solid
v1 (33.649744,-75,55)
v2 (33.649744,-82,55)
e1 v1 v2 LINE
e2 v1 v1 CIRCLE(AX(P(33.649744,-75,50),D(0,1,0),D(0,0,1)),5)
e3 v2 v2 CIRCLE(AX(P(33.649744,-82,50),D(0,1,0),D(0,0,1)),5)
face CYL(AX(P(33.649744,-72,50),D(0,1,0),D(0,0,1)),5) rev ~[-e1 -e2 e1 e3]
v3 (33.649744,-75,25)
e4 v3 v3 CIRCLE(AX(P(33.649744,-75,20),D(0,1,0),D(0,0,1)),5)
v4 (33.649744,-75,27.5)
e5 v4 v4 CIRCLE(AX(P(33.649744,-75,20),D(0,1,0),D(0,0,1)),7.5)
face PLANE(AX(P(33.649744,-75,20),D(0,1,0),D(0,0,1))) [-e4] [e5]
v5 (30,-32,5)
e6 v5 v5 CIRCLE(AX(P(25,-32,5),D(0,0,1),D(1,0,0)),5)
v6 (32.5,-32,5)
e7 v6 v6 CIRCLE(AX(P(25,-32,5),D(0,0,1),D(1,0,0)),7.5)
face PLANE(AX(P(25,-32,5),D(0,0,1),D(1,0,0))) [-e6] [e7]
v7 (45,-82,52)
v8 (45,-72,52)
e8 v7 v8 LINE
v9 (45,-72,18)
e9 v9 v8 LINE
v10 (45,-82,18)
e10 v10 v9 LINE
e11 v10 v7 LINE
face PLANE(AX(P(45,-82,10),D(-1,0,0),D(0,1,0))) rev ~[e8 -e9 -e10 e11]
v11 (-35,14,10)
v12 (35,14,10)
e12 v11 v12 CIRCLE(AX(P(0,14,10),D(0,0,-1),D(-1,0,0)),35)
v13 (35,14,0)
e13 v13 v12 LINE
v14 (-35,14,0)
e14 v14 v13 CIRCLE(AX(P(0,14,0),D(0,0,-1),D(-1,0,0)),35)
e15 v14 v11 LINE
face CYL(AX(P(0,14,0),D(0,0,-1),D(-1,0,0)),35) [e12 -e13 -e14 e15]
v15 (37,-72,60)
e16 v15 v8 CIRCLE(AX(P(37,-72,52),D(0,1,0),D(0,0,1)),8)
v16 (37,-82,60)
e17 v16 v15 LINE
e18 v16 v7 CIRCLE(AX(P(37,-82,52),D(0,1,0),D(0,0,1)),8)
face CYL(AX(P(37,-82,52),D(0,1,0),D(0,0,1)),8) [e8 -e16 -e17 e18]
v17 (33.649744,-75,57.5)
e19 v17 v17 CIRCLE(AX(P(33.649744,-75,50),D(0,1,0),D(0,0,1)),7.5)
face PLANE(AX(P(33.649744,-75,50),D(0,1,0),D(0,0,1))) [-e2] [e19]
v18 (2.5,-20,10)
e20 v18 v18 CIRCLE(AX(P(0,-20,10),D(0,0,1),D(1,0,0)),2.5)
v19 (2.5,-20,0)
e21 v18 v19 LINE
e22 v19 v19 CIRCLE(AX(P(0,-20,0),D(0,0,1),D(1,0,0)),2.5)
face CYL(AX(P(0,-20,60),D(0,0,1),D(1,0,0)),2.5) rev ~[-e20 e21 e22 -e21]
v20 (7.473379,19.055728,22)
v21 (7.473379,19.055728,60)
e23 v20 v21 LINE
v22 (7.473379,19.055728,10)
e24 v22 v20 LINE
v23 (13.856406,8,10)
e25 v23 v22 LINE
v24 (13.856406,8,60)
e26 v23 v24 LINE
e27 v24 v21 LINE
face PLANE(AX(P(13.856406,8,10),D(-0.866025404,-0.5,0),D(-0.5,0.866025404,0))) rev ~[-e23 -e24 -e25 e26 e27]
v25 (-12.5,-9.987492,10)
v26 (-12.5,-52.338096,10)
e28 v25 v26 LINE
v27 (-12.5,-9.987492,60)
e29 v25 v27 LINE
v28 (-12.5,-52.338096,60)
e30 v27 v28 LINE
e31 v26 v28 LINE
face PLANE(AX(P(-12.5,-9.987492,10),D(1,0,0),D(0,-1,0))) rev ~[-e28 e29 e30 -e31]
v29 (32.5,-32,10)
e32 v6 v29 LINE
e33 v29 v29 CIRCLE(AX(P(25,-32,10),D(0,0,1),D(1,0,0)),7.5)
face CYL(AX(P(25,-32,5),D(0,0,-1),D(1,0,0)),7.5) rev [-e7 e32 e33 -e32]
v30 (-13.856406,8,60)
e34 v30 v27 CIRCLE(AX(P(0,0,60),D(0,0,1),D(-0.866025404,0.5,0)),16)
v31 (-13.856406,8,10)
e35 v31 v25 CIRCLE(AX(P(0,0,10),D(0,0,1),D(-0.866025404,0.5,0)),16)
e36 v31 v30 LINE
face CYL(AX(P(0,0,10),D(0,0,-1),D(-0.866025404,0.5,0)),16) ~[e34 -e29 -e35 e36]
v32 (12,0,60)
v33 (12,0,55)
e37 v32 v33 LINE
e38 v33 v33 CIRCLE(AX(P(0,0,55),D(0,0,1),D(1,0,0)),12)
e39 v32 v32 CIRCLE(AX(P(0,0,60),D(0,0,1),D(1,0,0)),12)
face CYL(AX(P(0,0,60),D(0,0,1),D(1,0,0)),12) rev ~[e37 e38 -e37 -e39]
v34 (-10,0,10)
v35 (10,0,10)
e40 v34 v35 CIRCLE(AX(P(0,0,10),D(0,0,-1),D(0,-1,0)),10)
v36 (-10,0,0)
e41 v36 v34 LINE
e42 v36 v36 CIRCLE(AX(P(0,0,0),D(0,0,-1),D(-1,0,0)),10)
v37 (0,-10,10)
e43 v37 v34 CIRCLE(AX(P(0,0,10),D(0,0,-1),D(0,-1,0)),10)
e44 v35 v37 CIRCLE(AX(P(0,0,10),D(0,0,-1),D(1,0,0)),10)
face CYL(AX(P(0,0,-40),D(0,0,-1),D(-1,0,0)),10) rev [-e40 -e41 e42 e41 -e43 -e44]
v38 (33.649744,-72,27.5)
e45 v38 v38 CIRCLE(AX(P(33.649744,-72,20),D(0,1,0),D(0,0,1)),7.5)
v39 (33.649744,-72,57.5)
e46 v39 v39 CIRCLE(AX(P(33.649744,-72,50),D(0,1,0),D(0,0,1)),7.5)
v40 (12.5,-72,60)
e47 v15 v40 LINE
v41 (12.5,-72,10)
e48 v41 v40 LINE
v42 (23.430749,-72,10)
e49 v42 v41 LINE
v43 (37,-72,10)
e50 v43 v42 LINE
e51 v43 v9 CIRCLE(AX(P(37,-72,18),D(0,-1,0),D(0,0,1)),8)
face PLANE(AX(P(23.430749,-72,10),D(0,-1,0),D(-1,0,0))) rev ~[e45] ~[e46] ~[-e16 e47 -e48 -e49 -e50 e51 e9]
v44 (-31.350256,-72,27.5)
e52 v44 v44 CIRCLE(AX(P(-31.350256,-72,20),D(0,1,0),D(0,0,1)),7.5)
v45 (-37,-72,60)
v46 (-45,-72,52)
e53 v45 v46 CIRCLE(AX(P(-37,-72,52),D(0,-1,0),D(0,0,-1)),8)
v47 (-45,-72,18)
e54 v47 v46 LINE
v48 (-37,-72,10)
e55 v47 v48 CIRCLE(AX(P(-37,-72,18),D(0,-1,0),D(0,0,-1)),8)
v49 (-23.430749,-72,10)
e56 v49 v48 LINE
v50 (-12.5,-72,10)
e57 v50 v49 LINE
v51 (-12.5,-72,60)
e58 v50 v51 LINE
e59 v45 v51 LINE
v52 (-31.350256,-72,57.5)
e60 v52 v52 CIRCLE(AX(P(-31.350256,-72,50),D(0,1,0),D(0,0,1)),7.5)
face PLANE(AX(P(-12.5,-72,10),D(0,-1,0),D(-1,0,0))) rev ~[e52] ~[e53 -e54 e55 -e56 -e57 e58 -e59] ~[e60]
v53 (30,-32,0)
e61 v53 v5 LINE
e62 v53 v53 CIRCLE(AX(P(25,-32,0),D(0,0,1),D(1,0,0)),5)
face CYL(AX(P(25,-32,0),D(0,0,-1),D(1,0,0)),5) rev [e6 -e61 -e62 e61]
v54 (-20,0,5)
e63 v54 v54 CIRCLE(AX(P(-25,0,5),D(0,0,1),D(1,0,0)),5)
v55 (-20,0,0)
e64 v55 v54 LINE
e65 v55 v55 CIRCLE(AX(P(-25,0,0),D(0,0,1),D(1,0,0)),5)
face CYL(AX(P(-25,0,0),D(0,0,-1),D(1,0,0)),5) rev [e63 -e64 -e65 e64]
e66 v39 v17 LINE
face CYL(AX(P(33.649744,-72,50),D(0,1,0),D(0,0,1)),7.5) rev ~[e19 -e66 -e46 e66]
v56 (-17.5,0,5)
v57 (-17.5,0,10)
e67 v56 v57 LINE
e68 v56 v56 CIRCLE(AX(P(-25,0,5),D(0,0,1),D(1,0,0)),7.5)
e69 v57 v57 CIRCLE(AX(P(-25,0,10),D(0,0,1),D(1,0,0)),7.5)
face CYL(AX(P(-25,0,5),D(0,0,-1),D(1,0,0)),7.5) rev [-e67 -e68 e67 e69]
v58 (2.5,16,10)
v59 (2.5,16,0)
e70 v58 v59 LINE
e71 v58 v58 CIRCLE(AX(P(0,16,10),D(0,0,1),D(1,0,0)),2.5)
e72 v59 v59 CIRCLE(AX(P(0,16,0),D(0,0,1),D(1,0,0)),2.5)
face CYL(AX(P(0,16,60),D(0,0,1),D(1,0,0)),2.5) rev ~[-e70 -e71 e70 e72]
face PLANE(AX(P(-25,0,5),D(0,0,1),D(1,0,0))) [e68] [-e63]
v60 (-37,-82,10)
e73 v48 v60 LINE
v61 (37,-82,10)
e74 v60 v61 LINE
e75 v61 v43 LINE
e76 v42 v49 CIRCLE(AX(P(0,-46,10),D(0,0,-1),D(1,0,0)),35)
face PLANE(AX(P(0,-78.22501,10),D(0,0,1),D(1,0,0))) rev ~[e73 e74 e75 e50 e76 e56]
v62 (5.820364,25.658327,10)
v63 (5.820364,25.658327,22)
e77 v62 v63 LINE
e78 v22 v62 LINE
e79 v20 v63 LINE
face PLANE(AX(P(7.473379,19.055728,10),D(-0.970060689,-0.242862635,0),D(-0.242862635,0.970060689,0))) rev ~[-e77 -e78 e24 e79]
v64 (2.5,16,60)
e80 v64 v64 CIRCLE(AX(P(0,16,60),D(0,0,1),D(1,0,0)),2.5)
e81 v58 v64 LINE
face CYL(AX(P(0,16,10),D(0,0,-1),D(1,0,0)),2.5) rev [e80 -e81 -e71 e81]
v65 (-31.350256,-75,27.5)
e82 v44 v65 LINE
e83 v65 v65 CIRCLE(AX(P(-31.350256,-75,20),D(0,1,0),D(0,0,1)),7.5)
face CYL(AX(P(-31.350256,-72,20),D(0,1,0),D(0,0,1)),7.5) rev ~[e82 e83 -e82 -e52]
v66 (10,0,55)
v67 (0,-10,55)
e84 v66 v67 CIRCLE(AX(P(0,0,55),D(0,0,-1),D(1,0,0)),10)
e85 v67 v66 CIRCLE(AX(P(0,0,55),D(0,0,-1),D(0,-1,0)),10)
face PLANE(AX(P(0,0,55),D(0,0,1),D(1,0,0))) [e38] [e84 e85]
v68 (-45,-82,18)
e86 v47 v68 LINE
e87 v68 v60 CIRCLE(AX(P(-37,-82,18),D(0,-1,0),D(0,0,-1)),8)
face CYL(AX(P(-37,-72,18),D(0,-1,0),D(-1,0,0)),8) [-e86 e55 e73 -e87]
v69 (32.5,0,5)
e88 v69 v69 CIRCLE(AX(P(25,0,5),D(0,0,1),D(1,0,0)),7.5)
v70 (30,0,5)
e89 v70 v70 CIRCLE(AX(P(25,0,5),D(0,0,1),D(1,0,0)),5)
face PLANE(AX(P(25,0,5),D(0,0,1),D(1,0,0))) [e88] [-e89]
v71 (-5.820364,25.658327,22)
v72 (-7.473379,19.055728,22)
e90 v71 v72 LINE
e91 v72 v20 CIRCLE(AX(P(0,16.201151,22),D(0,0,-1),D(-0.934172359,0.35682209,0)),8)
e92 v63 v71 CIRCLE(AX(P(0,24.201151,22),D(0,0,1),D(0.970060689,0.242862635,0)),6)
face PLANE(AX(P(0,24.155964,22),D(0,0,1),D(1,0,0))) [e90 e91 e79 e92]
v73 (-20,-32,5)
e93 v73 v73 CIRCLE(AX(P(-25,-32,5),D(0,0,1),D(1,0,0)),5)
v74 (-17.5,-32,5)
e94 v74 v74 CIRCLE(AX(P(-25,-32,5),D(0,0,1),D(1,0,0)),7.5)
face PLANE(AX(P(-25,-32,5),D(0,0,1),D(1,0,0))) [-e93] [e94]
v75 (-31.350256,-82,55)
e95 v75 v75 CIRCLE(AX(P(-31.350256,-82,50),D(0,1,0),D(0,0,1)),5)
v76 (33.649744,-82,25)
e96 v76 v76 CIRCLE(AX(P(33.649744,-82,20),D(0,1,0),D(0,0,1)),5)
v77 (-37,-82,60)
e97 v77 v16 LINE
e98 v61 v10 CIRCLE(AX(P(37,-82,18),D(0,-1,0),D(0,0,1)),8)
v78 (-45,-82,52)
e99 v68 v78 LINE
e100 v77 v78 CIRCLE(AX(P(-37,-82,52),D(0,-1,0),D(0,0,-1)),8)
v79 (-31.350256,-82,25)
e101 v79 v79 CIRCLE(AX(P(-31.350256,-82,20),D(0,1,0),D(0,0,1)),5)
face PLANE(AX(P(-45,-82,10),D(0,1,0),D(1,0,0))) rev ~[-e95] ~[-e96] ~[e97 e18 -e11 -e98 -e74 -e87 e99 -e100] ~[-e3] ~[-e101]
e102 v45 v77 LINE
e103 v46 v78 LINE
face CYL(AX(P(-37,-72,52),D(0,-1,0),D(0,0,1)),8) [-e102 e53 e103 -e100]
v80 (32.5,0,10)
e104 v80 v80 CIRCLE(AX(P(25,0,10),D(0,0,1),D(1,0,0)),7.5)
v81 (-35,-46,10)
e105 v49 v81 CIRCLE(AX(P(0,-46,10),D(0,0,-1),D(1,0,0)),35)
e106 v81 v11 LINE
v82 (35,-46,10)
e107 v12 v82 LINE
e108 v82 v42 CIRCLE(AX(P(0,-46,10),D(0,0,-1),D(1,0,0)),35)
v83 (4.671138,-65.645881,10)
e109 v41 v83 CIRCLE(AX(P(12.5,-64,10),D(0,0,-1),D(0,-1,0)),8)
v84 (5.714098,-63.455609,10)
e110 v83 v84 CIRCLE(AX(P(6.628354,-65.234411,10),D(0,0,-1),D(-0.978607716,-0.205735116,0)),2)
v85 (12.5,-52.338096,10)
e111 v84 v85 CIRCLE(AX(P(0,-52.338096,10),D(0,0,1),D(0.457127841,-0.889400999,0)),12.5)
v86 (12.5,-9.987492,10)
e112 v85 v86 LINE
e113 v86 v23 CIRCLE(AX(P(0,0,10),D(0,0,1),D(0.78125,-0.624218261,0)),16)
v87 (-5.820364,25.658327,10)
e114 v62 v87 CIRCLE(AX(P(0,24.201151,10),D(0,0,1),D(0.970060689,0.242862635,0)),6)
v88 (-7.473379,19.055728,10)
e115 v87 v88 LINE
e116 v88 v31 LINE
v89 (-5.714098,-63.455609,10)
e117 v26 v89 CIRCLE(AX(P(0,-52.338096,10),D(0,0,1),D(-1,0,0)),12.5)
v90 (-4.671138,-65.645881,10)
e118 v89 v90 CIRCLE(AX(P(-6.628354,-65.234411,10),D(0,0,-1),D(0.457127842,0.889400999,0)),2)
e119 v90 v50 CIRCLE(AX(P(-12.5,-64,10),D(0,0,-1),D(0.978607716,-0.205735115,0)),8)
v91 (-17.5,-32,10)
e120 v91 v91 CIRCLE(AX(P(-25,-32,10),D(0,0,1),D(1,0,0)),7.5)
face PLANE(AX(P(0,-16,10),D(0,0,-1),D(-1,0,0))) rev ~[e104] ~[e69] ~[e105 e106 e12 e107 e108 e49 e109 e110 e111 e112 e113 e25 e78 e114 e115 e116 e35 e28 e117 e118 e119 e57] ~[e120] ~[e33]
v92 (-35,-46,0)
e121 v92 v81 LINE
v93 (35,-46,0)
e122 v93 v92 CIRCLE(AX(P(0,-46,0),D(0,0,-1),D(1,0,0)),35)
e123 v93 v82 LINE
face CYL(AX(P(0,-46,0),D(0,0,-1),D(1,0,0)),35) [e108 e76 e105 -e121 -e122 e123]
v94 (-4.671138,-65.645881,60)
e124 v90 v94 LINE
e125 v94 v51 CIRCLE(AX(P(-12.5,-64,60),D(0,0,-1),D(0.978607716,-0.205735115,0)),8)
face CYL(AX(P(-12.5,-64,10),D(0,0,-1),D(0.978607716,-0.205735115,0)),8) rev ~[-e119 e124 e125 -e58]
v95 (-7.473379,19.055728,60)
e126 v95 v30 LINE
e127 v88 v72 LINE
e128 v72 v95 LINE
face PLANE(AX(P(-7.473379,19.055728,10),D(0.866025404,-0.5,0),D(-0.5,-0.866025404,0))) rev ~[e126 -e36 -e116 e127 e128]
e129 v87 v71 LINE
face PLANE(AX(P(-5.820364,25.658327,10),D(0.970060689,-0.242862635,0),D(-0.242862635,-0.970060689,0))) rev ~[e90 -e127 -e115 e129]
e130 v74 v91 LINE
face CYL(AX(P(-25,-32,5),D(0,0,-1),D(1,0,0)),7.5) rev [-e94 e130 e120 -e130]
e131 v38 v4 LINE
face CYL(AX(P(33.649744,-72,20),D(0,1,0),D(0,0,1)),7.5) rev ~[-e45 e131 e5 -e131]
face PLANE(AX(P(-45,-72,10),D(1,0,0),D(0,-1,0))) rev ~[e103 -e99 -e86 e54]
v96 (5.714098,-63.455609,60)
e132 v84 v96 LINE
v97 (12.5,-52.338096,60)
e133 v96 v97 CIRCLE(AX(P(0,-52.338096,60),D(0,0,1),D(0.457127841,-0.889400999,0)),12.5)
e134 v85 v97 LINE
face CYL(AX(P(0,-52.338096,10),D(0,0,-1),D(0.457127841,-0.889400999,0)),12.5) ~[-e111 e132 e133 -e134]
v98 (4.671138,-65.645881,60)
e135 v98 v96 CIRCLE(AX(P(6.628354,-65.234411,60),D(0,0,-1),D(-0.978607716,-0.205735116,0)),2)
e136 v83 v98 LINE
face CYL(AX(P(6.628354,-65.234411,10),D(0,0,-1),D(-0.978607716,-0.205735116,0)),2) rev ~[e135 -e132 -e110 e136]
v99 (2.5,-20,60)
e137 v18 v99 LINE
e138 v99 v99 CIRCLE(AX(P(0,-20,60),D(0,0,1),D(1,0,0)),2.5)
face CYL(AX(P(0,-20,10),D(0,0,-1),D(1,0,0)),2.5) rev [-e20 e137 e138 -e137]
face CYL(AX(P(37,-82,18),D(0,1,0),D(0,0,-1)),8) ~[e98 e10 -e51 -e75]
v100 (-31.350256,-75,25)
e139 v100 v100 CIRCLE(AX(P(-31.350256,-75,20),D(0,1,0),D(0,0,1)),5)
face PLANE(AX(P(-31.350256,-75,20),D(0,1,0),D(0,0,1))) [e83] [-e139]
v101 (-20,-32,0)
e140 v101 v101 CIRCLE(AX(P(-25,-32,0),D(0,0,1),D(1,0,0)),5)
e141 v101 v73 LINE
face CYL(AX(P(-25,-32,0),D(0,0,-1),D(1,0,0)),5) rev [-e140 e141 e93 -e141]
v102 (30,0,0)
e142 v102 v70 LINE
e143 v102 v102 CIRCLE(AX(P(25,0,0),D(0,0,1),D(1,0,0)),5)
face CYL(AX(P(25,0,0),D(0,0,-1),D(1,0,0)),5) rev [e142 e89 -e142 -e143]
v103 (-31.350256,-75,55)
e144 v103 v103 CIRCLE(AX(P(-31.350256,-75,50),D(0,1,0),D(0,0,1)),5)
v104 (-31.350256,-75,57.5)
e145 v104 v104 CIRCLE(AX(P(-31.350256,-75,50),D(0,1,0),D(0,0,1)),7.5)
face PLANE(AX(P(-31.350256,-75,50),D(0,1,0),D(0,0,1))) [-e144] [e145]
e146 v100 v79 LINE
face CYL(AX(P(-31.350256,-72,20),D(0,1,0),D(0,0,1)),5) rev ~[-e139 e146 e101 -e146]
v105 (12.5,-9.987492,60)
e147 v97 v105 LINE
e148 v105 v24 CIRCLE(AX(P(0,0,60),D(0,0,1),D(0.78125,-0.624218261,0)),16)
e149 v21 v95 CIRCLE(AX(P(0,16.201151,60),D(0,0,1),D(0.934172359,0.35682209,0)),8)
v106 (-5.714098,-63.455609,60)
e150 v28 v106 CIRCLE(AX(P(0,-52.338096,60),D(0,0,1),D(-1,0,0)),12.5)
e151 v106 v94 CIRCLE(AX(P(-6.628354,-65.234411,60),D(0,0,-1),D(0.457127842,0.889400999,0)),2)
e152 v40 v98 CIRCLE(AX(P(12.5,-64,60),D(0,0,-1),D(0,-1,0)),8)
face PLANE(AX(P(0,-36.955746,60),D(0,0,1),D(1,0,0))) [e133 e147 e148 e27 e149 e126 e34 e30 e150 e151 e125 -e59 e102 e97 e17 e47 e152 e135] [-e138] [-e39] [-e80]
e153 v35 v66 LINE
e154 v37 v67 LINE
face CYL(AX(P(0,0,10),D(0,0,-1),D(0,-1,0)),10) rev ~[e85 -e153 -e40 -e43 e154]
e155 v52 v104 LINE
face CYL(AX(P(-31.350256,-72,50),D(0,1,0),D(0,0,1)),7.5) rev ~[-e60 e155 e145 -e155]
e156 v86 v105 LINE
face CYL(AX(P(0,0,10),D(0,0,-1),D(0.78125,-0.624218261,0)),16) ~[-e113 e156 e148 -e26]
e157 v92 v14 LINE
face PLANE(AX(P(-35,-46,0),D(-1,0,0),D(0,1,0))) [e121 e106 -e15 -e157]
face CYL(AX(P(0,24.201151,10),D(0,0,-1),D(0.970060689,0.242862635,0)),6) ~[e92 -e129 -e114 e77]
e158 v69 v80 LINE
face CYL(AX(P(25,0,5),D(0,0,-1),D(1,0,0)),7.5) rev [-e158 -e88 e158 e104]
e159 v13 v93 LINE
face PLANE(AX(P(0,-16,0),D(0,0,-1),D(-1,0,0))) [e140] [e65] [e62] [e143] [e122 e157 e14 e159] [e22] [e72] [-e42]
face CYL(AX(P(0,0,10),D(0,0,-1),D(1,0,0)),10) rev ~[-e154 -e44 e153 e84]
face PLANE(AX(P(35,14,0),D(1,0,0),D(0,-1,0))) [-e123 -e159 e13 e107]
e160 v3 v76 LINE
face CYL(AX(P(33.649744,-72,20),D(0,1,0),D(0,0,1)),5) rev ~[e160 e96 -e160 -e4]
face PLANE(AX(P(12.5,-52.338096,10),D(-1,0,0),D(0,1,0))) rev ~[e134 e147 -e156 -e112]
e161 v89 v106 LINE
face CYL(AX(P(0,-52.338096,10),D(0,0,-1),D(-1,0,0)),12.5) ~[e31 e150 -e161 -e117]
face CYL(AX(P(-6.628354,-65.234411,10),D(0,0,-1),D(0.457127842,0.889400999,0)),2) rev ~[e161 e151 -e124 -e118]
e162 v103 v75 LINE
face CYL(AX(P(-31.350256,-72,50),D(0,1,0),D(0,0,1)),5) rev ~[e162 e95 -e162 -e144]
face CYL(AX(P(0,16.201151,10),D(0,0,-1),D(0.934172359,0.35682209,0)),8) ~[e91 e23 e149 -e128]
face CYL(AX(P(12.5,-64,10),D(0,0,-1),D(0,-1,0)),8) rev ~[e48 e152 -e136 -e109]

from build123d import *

# Parameters (mm, degrees)
FLANGE_PLATE_SKETCH_R     = 5
FLANGE_PLATE_DEPTH        = 10
FLANGE_START              = -5
FLANGE_RECESS_SKETCH_R    = 7.5
FLANGE_RECESS_SKETCH_R_2  = 5
FLANGE_RECESS_5MM_DEPTH   = 5
BRACKET_BODY_SKETCH_R     = 2.5
BRACKET_BODY_DEPTH        = 50
THROUGH_START             = -50
THROUGH_BORE_SKETCH_R     = 10
THROUGH_BORE_DEPTH        = 50
BORE_COUNTERBORE_SKETCH_R = 12
BORE_COUNTERBORE_24_DEPTH = 5
BODY_POCKET_SKETCH_R      = 5
BODY_POCKET_20MM_DEPTH    = 20
POCKET_STEP_SKETCH_R      = 7.5
POCKET_STEP_3MM_DEPTH     = 3
BODY_BOSS_12MM_DEPTH      = 12
BODY_FILLET_R8_A_R        = 8
BODY_FILLET_R8_B_R        = 8
BODY_SLOT_SKETCH_R        = 2.5
BODY_SLOT_CUT_DEPTH       = 112.126054551


with BuildPart() as part:
    # Flange Plate Sketch → Flange Plate (new body)
    with BuildSketch(Plane.XY):
        with BuildLine():
            Line((-35, -46), (-35, 14))
            ThreePointArc((-35, 14), (0, 49), (35, 14))
            Line((35, 14), (35, -46))
            ThreePointArc((35, -46), (0, -81), (-35, -46))
        make_face()
        with Locations((-25, 0)):
            Circle(FLANGE_PLATE_SKETCH_R, mode=Mode.SUBTRACT)
        with Locations((25, 0)):
            Circle(FLANGE_PLATE_SKETCH_R, mode=Mode.SUBTRACT)
        with Locations((-25, -32)):
            Circle(FLANGE_PLATE_SKETCH_R, mode=Mode.SUBTRACT)
        with Locations((25, -32)):
            Circle(FLANGE_PLATE_SKETCH_R, mode=Mode.SUBTRACT)
    extrude(amount=FLANGE_PLATE_DEPTH)

    # Flange Recess Sketch → Flange Recess 5mm (cut)
    # profile 1 of 4: a face of its own
    with BuildSketch(Plane.XY.offset(10).offset(FLANGE_START)):
        with Locations((-25, 0)):
            Circle(FLANGE_RECESS_SKETCH_R)
        with Locations((-25, 0)):
            Circle(FLANGE_RECESS_SKETCH_R_2, mode=Mode.SUBTRACT)
    # profile 2 of 4: a face of its own
    with BuildSketch(Plane.XY.offset(10).offset(FLANGE_START)):
        with Locations((25, 0)):
            Circle(FLANGE_RECESS_SKETCH_R)
        with Locations((25, 0)):
            Circle(FLANGE_RECESS_SKETCH_R_2, mode=Mode.SUBTRACT)
    # profile 3 of 4: a face of its own
    with BuildSketch(Plane.XY.offset(10).offset(FLANGE_START)):
        with Locations((25, -32)):
            Circle(FLANGE_RECESS_SKETCH_R)
        with Locations((25, -32)):
            Circle(FLANGE_RECESS_SKETCH_R_2, mode=Mode.SUBTRACT)
    # profile 4 of 4: a face of its own
    with BuildSketch(Plane.XY.offset(10).offset(FLANGE_START)):
        with Locations((-25, -32)):
            Circle(FLANGE_RECESS_SKETCH_R)
        with Locations((-25, -32)):
            Circle(FLANGE_RECESS_SKETCH_R_2, mode=Mode.SUBTRACT)
    extrude(amount=FLANGE_RECESS_5MM_DEPTH, mode=Mode.SUBTRACT)

    # Bracket Body Sketch → Bracket Body (add)
    # profile 1 of 2: a face of its own
    with BuildSketch(Plane.XY.offset(10)):
        with BuildLine():
            Line((-12.5, -72), (-23.430749028, -72))
            ThreePointArc((-23.430749028, -72), (0, -81), (23.430749028, -72))
            Line((23.430749028, -72), (12.5, -72))
            ThreePointArc((12.5, -72), (7.458524391, -70.211563707), (4.67113827, -65.645880922))
            ThreePointArc((4.67113827, -65.645880922), (4.822624016, -64.374561693), (5.714098019, -63.455608694))
            ThreePointArc((5.714098019, -63.455608694), (10.669494488, -58.85053718), (12.5, -52.33809621))
            Line((12.5, -52.33809621), (12.5, -9.987492178))
            ThreePointArc((12.5, -9.987492178), (15.954701786, -1.203117164), (13.856406461, 8))
            Line((13.856406461, 8), (7.473378872, 19.05572809))
            ThreePointArc((7.473378872, 19.05572809), (0, 24.201151372), (-7.473378872, 19.05572809))
            Line((-7.473378872, 19.05572809), (-13.856406461, 8))
            ThreePointArc((-13.856406461, 8), (-15.954701786, -1.203117164), (-12.5, -9.987492178))
            Line((-12.5, -9.987492178), (-12.5, -52.33809621))
            ThreePointArc((-12.5, -52.33809621), (-10.669494488, -58.85053718), (-5.714098019, -63.455608694))
            ThreePointArc((-5.714098019, -63.455608694), (-4.822624016, -64.374561693), (-4.67113827, -65.645880922))
            ThreePointArc((-4.67113827, -65.645880922), (-7.458524391, -70.211563707), (-12.5, -72))
        make_face()
        with Locations((0, -20)):
            Circle(BRACKET_BODY_SKETCH_R, mode=Mode.SUBTRACT)
        with BuildLine():
            ThreePointArc((0, -10), (-7.071067812, 7.071067812), (10, 0))
            ThreePointArc((10, 0), (7.071067812, -7.071067812), (0, -10))
        make_face(mode=Mode.SUBTRACT)
        with Locations((0, 16)):
            Circle(BRACKET_BODY_SKETCH_R, mode=Mode.SUBTRACT)
    # profile 2 of 2: a face of its own
    with BuildSketch(Plane.XY.offset(10)):
        with BuildLine():
            Line((-45, -72), (-45, -82))
            Line((-45, -82), (45, -82))
            Line((45, -82), (45, -72))
            Line((45, -72), (23.430749028, -72))
            ThreePointArc((23.430749028, -72), (0, -81), (-23.430749028, -72))
            Line((-23.430749028, -72), (-45, -72))
        make_face()
    extrude(amount=BRACKET_BODY_DEPTH)

    # Through Bore Sketch → Through Bore (cut)
    with BuildSketch(Plane.XY.offset(10).offset(THROUGH_START)):
        with Locations(Location((0, 0, 0), (0, 0, 180))):
            Circle(THROUGH_BORE_SKETCH_R)
    extrude(amount=THROUGH_BORE_DEPTH, mode=Mode.SUBTRACT)

    # Bore Counterbore Sketch → Bore Counterbore Ø24 (cut)
    with BuildSketch(Plane.XY.offset(60)):
        Circle(BORE_COUNTERBORE_SKETCH_R)
    extrude(amount=-BORE_COUNTERBORE_24_DEPTH, mode=Mode.SUBTRACT)

    # Body Pocket Sketch → Body Pocket 20mm (cut)
    with BuildSketch(Plane(origin=(0, -72, 0), x_dir=(1, 0, 0), z_dir=(0, 1, 0))):
        with Locations(Location((-31.350256263, -20, 0), (0, 0, 270))):
            Circle(BODY_POCKET_SKETCH_R)
        with Locations(Location((-31.350256263, -50, 0), (0, 0, 270))):
            Circle(BODY_POCKET_SKETCH_R)
        with Locations(Location((33.649743737, -20, 0), (0, 0, 270))):
            Circle(BODY_POCKET_SKETCH_R)
        with Locations(Location((33.649743737, -50, 0), (0, 0, 270))):
            Circle(BODY_POCKET_SKETCH_R)
    extrude(amount=-BODY_POCKET_20MM_DEPTH, mode=Mode.SUBTRACT)

    # Pocket Step Sketch → Pocket Step 3mm (cut)
    with BuildSketch(Plane(origin=(0, -72, 0), x_dir=(1, 0, 0), z_dir=(0, 1, 0))):
        with Locations(Location((-31.350256263, -20, 0), (0, 0, 270))):
            Circle(POCKET_STEP_SKETCH_R)
        with Locations(Location((-31.350256263, -50, 0), (0, 0, 270))):
            Circle(POCKET_STEP_SKETCH_R)
        with Locations(Location((33.649743737, -20, 0), (0, 0, 270))):
            Circle(POCKET_STEP_SKETCH_R)
        with Locations(Location((33.649743737, -50, 0), (0, 0, 270))):
            Circle(POCKET_STEP_SKETCH_R)
    extrude(amount=-POCKET_STEP_3MM_DEPTH, mode=Mode.SUBTRACT)

    # Body Boss Sketch → Body Boss 12mm (add)
    with BuildSketch(Plane.XY.offset(10)):
        with BuildLine():
            Line((7.473378872, 19.05572809), (5.820364134, 25.658327183))
            ThreePointArc((5.820364134, 25.658327183), (0, 30.201151372), (-5.820364134, 25.658327183))
            Line((-5.820364134, 25.658327183), (-7.473378872, 19.05572809))
            ThreePointArc((-7.473378872, 19.05572809), (0, 24.201151372), (7.473378872, 19.05572809))
        make_face()
    extrude(amount=BODY_BOSS_12MM_DEPTH)

    # Body Fillet R8 A
    body_fillet_r8_a_edges = [part.edges().sort_by_distance(p)[0] for p in [
        (-45, -77, 60),
        (45, -77, 60),
    ]]
    fillet(body_fillet_r8_a_edges, radius=BODY_FILLET_R8_A_R)

    # Body Fillet R8 B
    body_fillet_r8_b_edges = [part.edges().sort_by_distance(p)[0] for p in [
        (-45, -77, 10),
        (45, -77, 10),
    ]]
    fillet(body_fillet_r8_b_edges, radius=BODY_FILLET_R8_B_R)

    # Body Slot Sketch → Body Slot Cut (cut, through all)
    with BuildSketch(Plane.XY.offset(60)):
        with Locations((0, 16)):
            Circle(BODY_SLOT_SKETCH_R)
        with Locations((0, -20)):
            Circle(BODY_SLOT_SKETCH_R)
    extrude(amount=-BODY_SLOT_CUT_DEPTH, mode=Mode.SUBTRACT)


solid = part.part
